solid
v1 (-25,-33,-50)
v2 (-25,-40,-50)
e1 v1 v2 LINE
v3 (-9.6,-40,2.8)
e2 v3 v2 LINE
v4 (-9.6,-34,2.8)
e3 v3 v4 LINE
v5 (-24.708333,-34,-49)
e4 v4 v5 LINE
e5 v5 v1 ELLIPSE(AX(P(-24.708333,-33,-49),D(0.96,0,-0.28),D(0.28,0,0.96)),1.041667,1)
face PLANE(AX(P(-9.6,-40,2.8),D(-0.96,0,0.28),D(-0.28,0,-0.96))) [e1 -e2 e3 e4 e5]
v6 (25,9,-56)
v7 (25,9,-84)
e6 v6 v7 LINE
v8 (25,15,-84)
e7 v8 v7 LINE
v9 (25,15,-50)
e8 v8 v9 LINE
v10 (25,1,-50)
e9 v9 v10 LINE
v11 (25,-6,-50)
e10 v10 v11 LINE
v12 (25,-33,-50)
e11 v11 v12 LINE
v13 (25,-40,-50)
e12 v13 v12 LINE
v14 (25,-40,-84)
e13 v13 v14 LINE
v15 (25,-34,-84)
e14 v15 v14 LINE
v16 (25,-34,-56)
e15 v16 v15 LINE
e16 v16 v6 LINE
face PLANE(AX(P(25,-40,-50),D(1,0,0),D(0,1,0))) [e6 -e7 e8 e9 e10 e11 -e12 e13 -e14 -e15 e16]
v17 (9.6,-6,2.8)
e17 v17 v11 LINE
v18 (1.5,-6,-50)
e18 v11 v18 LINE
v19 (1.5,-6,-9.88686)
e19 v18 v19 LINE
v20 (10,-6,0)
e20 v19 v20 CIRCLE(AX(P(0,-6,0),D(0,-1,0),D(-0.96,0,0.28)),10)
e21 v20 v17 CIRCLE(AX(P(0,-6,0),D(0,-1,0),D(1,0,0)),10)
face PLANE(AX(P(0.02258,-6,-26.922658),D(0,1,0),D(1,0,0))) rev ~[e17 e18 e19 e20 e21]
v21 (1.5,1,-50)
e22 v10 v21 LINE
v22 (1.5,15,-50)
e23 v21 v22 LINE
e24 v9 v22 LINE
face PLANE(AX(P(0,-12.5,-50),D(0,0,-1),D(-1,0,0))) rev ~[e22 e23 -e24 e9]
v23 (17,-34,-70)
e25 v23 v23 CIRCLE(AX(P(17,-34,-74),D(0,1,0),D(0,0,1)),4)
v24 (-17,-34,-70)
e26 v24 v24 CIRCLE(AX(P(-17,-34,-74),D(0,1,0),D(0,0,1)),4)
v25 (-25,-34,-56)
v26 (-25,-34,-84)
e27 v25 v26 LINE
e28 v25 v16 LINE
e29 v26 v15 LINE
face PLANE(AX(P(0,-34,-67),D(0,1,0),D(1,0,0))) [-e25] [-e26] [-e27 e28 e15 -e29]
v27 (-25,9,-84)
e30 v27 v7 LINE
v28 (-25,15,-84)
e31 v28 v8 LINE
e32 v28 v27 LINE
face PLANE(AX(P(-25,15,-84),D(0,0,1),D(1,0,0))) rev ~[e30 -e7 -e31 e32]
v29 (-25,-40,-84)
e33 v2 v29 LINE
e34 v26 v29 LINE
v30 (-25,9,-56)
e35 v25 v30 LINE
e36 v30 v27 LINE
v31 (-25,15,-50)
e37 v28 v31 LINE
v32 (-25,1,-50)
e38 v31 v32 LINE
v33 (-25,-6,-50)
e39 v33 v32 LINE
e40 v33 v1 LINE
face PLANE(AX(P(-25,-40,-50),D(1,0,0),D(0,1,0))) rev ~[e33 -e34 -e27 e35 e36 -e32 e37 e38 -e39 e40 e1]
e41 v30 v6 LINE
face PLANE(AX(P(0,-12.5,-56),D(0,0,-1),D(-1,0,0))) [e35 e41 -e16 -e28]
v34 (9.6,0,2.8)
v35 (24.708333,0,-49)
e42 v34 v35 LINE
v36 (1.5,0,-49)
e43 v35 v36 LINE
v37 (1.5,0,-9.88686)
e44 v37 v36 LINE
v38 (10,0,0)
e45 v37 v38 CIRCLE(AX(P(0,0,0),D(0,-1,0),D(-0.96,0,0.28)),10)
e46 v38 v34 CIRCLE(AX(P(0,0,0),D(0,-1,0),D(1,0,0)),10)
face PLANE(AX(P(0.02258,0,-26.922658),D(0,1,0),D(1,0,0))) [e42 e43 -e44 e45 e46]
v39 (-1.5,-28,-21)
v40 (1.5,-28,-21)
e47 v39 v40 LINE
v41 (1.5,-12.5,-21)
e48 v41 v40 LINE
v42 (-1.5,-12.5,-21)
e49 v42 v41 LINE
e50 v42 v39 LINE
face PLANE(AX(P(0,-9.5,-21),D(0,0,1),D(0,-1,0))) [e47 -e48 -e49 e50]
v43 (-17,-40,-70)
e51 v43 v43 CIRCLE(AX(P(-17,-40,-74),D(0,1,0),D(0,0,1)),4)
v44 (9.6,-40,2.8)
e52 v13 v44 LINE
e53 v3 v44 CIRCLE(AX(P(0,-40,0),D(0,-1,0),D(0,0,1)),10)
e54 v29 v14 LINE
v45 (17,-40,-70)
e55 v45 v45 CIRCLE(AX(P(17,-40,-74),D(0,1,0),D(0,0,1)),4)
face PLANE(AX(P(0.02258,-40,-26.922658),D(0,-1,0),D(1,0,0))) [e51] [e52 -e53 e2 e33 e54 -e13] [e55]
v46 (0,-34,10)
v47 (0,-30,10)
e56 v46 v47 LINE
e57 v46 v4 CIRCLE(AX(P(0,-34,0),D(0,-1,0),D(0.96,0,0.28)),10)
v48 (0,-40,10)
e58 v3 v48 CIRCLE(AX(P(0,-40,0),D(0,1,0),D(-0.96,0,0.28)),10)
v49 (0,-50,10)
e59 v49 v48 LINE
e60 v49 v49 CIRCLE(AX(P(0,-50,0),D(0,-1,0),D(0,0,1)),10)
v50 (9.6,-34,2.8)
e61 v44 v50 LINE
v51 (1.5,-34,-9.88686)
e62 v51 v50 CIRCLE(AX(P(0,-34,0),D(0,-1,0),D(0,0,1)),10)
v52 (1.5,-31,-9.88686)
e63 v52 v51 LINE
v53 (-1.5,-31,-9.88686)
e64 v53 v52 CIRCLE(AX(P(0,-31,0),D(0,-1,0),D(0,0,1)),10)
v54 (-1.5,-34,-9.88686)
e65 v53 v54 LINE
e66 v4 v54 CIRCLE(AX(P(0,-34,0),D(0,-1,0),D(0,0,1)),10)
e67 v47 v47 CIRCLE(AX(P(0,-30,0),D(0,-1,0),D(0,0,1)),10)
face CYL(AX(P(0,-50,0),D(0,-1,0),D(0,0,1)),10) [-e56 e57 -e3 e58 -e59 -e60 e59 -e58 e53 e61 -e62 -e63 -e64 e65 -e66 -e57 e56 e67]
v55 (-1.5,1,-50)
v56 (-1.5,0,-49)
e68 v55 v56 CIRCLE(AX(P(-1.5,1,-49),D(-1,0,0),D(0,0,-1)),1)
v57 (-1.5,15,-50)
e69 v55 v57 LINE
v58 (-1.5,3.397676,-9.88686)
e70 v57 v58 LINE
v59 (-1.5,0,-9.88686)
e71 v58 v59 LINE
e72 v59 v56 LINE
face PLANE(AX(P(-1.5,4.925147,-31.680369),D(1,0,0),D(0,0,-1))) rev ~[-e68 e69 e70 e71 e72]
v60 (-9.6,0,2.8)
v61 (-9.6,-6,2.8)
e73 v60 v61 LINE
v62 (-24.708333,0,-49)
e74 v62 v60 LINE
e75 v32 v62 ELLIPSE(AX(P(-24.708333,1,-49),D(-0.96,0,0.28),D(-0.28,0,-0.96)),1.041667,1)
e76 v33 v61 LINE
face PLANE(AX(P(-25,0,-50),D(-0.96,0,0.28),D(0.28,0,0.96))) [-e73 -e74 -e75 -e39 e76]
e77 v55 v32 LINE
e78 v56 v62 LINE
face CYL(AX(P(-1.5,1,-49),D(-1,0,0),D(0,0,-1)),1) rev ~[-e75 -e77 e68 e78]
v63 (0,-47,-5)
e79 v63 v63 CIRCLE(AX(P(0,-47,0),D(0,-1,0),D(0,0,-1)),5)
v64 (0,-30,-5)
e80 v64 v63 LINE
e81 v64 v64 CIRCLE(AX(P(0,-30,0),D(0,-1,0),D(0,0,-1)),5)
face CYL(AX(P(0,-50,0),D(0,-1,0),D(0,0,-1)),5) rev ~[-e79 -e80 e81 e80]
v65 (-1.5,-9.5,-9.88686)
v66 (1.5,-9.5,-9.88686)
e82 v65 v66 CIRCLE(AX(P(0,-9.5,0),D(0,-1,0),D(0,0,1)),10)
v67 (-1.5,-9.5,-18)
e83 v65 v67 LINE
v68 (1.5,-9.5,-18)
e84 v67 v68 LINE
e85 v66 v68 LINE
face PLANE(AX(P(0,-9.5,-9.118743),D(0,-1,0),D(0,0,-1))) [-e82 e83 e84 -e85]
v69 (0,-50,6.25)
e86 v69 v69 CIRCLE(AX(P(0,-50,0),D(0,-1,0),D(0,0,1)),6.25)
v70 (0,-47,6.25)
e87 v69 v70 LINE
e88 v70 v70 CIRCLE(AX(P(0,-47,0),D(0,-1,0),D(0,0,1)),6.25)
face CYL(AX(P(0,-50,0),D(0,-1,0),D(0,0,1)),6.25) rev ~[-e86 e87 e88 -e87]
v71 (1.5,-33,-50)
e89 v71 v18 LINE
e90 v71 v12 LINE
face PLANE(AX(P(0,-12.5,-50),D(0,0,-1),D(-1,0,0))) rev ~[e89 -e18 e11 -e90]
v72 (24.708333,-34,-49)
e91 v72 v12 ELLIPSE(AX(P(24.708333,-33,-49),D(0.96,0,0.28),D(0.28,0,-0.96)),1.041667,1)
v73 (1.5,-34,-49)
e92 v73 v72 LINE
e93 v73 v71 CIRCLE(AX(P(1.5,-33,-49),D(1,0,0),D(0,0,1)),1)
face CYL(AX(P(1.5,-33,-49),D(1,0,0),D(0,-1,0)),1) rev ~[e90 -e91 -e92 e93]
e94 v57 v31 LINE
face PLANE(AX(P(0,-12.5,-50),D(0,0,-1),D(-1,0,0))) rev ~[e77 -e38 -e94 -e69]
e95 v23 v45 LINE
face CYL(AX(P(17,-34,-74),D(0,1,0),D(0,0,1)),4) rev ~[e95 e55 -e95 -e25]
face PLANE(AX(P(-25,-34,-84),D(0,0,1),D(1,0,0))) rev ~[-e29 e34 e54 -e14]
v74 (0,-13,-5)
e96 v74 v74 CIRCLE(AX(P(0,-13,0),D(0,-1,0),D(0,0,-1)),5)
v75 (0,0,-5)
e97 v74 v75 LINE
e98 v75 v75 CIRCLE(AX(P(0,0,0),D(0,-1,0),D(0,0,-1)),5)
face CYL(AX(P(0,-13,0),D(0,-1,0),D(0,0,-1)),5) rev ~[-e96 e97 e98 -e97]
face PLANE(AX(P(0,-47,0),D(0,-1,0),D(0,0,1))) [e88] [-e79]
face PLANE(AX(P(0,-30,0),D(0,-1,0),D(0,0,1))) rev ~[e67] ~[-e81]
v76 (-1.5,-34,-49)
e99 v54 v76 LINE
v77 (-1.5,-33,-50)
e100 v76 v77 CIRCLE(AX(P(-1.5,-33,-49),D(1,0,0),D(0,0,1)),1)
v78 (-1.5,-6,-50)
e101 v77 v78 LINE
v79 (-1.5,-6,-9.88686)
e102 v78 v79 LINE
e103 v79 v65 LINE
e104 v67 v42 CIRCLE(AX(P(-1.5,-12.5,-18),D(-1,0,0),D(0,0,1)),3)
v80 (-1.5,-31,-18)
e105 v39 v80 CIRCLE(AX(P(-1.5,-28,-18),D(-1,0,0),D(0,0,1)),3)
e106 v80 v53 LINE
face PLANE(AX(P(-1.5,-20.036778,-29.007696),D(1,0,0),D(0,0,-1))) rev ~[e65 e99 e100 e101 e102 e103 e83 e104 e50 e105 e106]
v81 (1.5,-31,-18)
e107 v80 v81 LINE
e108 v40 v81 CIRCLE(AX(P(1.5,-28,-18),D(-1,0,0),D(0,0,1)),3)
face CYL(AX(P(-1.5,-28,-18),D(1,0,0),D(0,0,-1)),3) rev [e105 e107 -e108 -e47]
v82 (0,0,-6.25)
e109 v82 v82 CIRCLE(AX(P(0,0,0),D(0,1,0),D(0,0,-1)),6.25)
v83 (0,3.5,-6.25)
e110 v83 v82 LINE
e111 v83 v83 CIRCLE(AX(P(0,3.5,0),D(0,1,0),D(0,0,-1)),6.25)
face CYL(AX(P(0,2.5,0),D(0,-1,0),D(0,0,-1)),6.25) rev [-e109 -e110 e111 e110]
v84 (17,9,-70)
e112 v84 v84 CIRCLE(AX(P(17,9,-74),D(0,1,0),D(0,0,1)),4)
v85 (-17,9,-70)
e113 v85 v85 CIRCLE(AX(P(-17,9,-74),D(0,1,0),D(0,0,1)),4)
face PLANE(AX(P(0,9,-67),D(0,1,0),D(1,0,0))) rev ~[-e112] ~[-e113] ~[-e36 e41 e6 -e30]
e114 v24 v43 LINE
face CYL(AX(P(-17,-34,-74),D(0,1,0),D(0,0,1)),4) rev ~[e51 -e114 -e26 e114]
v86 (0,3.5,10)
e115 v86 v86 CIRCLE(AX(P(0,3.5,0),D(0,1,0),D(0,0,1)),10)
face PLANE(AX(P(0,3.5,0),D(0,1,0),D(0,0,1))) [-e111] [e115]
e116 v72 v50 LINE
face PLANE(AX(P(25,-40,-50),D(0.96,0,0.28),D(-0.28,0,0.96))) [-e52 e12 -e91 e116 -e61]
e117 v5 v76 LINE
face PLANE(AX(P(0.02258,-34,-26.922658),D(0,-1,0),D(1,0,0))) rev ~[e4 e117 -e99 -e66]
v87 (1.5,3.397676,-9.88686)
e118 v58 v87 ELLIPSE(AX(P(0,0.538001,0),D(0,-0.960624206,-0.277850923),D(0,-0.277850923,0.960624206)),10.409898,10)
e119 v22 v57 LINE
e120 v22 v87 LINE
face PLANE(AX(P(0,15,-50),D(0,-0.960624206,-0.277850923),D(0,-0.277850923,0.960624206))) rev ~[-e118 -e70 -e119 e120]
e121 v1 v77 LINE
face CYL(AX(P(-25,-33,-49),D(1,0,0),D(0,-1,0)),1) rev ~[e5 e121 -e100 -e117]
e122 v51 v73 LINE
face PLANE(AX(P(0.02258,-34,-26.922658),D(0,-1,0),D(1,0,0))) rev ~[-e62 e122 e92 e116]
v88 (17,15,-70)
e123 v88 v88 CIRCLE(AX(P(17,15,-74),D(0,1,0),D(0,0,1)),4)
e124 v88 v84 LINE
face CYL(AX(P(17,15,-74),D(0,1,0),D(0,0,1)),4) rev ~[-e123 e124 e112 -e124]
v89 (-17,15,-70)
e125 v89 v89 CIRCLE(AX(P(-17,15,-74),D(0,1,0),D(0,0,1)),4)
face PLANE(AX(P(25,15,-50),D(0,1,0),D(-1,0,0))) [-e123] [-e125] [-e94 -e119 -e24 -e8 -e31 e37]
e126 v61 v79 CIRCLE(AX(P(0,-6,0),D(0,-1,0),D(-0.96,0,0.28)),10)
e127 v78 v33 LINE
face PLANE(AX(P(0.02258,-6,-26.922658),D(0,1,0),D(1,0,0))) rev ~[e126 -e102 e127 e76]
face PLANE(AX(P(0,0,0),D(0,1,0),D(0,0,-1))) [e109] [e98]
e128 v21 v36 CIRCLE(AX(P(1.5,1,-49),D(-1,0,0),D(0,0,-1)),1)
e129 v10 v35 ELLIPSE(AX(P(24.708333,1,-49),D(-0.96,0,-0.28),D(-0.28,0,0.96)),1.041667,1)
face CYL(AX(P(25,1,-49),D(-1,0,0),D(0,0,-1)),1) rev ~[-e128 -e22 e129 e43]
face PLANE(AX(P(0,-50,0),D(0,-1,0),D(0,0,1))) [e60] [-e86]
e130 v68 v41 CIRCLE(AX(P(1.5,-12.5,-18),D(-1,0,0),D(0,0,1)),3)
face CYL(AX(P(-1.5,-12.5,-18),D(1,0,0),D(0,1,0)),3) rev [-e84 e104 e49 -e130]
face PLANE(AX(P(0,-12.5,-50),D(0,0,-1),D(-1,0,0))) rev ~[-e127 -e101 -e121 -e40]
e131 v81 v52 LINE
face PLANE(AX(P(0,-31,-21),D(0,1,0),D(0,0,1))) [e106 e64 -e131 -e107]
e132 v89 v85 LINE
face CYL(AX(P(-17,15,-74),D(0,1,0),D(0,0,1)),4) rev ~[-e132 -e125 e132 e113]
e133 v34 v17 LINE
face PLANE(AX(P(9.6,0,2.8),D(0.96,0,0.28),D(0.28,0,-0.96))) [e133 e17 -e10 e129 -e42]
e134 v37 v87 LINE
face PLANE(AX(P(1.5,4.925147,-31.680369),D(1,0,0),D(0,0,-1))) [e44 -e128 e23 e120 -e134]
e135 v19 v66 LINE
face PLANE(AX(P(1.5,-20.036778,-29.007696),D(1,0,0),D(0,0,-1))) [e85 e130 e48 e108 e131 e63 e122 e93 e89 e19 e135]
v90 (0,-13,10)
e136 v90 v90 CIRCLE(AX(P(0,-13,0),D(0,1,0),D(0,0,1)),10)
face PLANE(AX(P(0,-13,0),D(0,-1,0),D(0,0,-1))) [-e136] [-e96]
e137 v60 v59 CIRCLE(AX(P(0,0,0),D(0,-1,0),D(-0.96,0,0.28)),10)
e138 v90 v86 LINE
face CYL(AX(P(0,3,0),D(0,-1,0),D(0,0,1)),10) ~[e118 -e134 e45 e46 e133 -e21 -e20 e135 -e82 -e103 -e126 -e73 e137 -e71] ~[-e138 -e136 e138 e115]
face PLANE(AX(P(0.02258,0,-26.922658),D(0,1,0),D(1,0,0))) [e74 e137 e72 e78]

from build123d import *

# Parameters (mm, degrees)
BASE_PROFILE_SKETCH_R        = 10
BASE_PROFILE_SKETCH_R_2      = 6.25
BASE_PLATE_3MM_DEPTH         = 3
MOUNTING_WEB_6MM_DEPTH       = 6
BASE_START                   = -13
SKETCH1_4_R                  = 10
SKETCH1_4_R_2                = 6.25
BASE_BLOCK_13MM_DEPTH        = 13
SIDE_WALL_SKETCH_W           = 50
SIDE_WALL_SKETCH_H           = 55
SIDE_WALL_6MM_DEPTH          = 6
GUSSET_PROFILE_SKETCH_W      = 50
GUSSET_PROFILE_SKETCH_H      = 34
GUSSET_PROFILE_SKETCH_R      = 4
GUSSET_A_6MM_DEPTH           = 6
GUSSET_START                 = -49
SKETCH3_2_W                  = 50
SKETCH3_2_H                  = 34
SKETCH3_2_R                  = 4
GUSSET_B_6MM_DEPTH           = 6
CLEVIS_EYE_SKETCH_R          = 10
CLEVIS_EYE_SKETCH_R_2        = 5
CLEVIS_EYE_ARM_6MM_DEPTH     = 6
SKETCH4_3_R                  = 10
SKETCH4_3_R_2                = 5
CLEVIS_EYE_BOSS_A_10MM_DEPTH = 10
CLEVIS_START                 = 10
SKETCH4_4_R                  = 10
SKETCH4_4_R_2                = 5
CLEVIS_EYE_BOSS_B_10MM_DEPTH = 10
CLEVIS_PIVOT_BORE_SKETCH_R   = 6.25
CLEVIS_PIVOT_BORE_CUT_DEPTH  = 3
LOWER_PIVOT_BOSS_SKETCH_R    = 6.25
LOWER_PIVOT_BOSS_SKETCH_R_2  = 5
LOWER_PIVOT_BOSS_16MM_DEPTH  = 16
LOWER_START                  = -3
LOWER_PIVOT_BORE_SKETCH_R    = 6.25
LOWER_PIVOT_BORE_CUT_DEPTH   = 3
SUPPORT_RIB_3MM_DEPTH        = 1.5
SPOT_FACE_PAD_SKETCH_R       = 10
SPOT_FACE_PAD_0_5MM_DEPTH    = 0.5
PAD_START                    = -1
PAD_RECESS_SKETCH_R          = 6.25
PAD_RECESS_1MM_DEPTH         = 1
CLEVIS_EDGE_FILLET_R1_R      = 1
RIB_EDGE_FILLET_R3_R         = 3


with BuildPart() as part:
    # Base Profile Sketch → Base Plate 3mm (new body)
    with BuildSketch(Plane(origin=(0, 0, 0), x_dir=(1, 0, 0), z_dir=(0, 1, 0))):
        with Locations(Location((0, 0, 0), (0, 0, 270))):
            Circle(BASE_PROFILE_SKETCH_R)
        with Locations(Location((0, 0, 0), (0, 0, 270))):
            Circle(BASE_PROFILE_SKETCH_R_2, mode=Mode.SUBTRACT)
    extrude(amount=BASE_PLATE_3MM_DEPTH)



with BuildPart() as body_2:
    # Sketch1_3 → Mounting Web 6mm (new body)
    with BuildSketch(Plane(origin=(0, 0, 0), x_dir=(1, 0, 0), z_dir=(0, 1, 0))):
        with BuildLine():
            Line((25, 50), (-25, 50))
            Line((-25, 50), (-9.6, -2.8))
            ThreePointArc((-9.6, -2.8), (-1.414213562, 9.899494937), (10, 0))
            ThreePointArc((10, 0), (9.899494937, -1.414213562), (9.6, -2.8))
            Line((9.6, -2.8), (25, 50))
        make_face()
    extrude(amount=-MOUNTING_WEB_6MM_DEPTH)


with BuildPart() as part_1:
    add(part.part)

    add(body_2.part)  # Base Block 13mm merges body 2
    # Sketch1_4 → Base Block 13mm (add)
    with BuildSketch(Plane(origin=(0, 0, 0), x_dir=(1, 0, 0), z_dir=(0, 1, 0)).offset(BASE_START)):
        with Locations(Location((0, 0, 0), (0, 0, 270))):
            Circle(SKETCH1_4_R)
        with Locations(Location((0, 0, 0), (0, 0, 270))):
            Circle(SKETCH1_4_R_2, mode=Mode.SUBTRACT)
    extrude(amount=BASE_BLOCK_13MM_DEPTH)

    # Side Wall Sketch → Side Wall 6mm (add)
    with BuildSketch(Plane(origin=(0, 0, -50), x_dir=(-1, 0, 0), z_dir=(0, 0, -1))):
        with Locations((0, -12.5)):
            Rectangle(SIDE_WALL_SKETCH_W, SIDE_WALL_SKETCH_H)
    extrude(amount=SIDE_WALL_6MM_DEPTH)

    # Gusset Profile Sketch → Gusset A 6mm (add)
    with BuildSketch(Plane(origin=(0, 15, 0), x_dir=(1, 0, 0), z_dir=(0, 1, 0))):
        with Locations((0, 67)):
            Rectangle(GUSSET_PROFILE_SKETCH_W, GUSSET_PROFILE_SKETCH_H)
        with Locations(Location((-17, 74, 0), (0, 0, 270))):
            Circle(GUSSET_PROFILE_SKETCH_R, mode=Mode.SUBTRACT)
        with Locations(Location((17, 74, 0), (0, 0, 270))):
            Circle(GUSSET_PROFILE_SKETCH_R, mode=Mode.SUBTRACT)
    extrude(amount=-GUSSET_A_6MM_DEPTH)

    # Sketch3_2 → Gusset B 6mm (add)
    with BuildSketch(Plane(origin=(0, 15, 0), x_dir=(1, 0, 0), z_dir=(0, 1, 0)).offset(GUSSET_START)):
        with Locations((0, 67)):
            Rectangle(SKETCH3_2_W, SKETCH3_2_H)
        with Locations(Location((-17, 74, 0), (0, 0, 270))):
            Circle(SKETCH3_2_R, mode=Mode.SUBTRACT)
        with Locations(Location((17, 74, 0), (0, 0, 270))):
            Circle(SKETCH3_2_R, mode=Mode.SUBTRACT)
    extrude(amount=-GUSSET_B_6MM_DEPTH)

    # Clevis Eye Sketch → Clevis Eye Arm 6mm (add)
    # profile 1 of 2: a face of its own
    with BuildSketch(Plane.XZ.offset(40)):
        with BuildLine():
            Line((-9.6, 2.8), (-25, -50))
            Line((-25, -50), (25, -50))
            Line((25, -50), (9.6, 2.8))
            ThreePointArc((9.6, 2.8), (9.899494937, 1.414213562), (10, 0))
            ThreePointArc((10, 0), (-1.414213562, -9.899494937), (-9.6, 2.8))
        make_face()
    # profile 2 of 2: a face of its own
    with BuildSketch(Plane.XZ.offset(40)):
        with Locations(Location((0, 0, 0), (0, 0, 90))):
            Circle(CLEVIS_EYE_SKETCH_R)
        with Locations(Location((0, 0, 0), (0, 0, 270))):
            Circle(CLEVIS_EYE_SKETCH_R_2, mode=Mode.SUBTRACT)
    extrude(amount=-CLEVIS_EYE_ARM_6MM_DEPTH)

    # Sketch4_3 → Clevis Eye Boss A 10mm (add)
    with BuildSketch(Plane.XZ.offset(40)):
        with Locations(Location((0, 0, 0), (0, 0, 90))):
            Circle(SKETCH4_3_R)
        with Locations(Location((0, 0, 0), (0, 0, 270))):
            Circle(SKETCH4_3_R_2, mode=Mode.SUBTRACT)
    extrude(amount=-CLEVIS_EYE_BOSS_A_10MM_DEPTH)

    # Sketch4_4 → Clevis Eye Boss B 10mm (add)
    with BuildSketch(Plane.XZ.offset(40).offset(CLEVIS_START)):
        with Locations(Location((0, 0, 0), (0, 0, 90))):
            Circle(SKETCH4_4_R)
        with Locations(Location((0, 0, 0), (0, 0, 270))):
            Circle(SKETCH4_4_R_2, mode=Mode.SUBTRACT)
    extrude(amount=-CLEVIS_EYE_BOSS_B_10MM_DEPTH)

    # Clevis Pivot Bore Sketch → Clevis Pivot Bore Cut (cut)
    with BuildSketch(Plane.XZ.offset(50)):
        with Locations(Location((0, 0, 0), (0, 0, 90))):
            Circle(CLEVIS_PIVOT_BORE_SKETCH_R)
    extrude(amount=-CLEVIS_PIVOT_BORE_CUT_DEPTH, mode=Mode.SUBTRACT)

    # Lower Pivot Boss Sketch → Lower Pivot Boss 16mm (add)
    with BuildSketch(Plane.XZ.offset(13)):
        with Locations(Location((0, 0, 0), (0, 0, 270))):
            Circle(LOWER_PIVOT_BOSS_SKETCH_R)
        with Locations(Location((0, 0, 0), (0, 0, 270))):
            Circle(LOWER_PIVOT_BOSS_SKETCH_R_2, mode=Mode.SUBTRACT)
    extrude(amount=-LOWER_PIVOT_BOSS_16MM_DEPTH)

    # Lower Pivot Bore Sketch → Lower Pivot Bore Cut (cut)
    with BuildSketch(Plane(origin=(0, 3, 0), x_dir=(1, 0, 0), z_dir=(0, 1, 0)).offset(LOWER_START)):
        with Locations(Location((0, 0, 0), (0, 0, 90))):
            Circle(LOWER_PIVOT_BORE_SKETCH_R)
    extrude(amount=LOWER_PIVOT_BORE_CUT_DEPTH, mode=Mode.SUBTRACT)

    # Support Rib Sketch → Support Rib 3mm (add, symmetric)
    with BuildSketch(Plane(origin=(0, 0, 0), x_dir=(0, 0, -1), z_dir=(1, 0, 0))):
        Polygon((50, 15), (8.511959117, 3), (8.511959117, 0), (50, 0), align=None)
        Polygon((9.118743045, -9.5), (21, -9.5), (21, -31), (9.118743045, -31), (9.118743045, -34), (50, -34), (50, -6), (9.118743045, -6), align=None)
    extrude(amount=SUPPORT_RIB_3MM_DEPTH, both=True)

    # Spot Face Pad Sketch → Spot Face Pad 0.5mm (add)
    with BuildSketch(Plane(origin=(0, 3, 0), x_dir=(1, 0, 0), z_dir=(0, 1, 0))):
        with Locations(Location((0, 0, 0), (0, 0, 270))):
            Circle(SPOT_FACE_PAD_SKETCH_R)
    extrude(amount=SPOT_FACE_PAD_0_5MM_DEPTH)

    # Pad Recess Sketch → Pad Recess 1mm (cut)
    with BuildSketch(Plane(origin=(0, 3.5, 0), x_dir=(1, 0, 0), z_dir=(0, 1, 0)).offset(PAD_START)):
        with Locations(Location((0, 0, 0), (0, 0, 90))):
            Circle(PAD_RECESS_SKETCH_R)
    extrude(amount=PAD_RECESS_1MM_DEPTH, mode=Mode.SUBTRACT)

    # Clevis Edge Fillet R1
    clevis_edge_fillet_r1_edges = [part_1.edges().sort_by_distance(p)[0] for p in [
        (13.25, 0, -50),
        (-13.25, 0, -50),
        (-13.25, -34, -50),
        (13.25, -34, -50),
    ]]
    fillet(clevis_edge_fillet_r1_edges, radius=CLEVIS_EDGE_FILLET_R1_R)

    # Rib Edge Fillet R3
    rib_edge_fillet_r3_edges = [part_1.edges().sort_by_distance(p)[0] for p in [
        (0, -9.5, -21),
        (0, -31, -21),
    ]]
    fillet(rib_edge_fillet_r3_edges, radius=RIB_EDGE_FILLET_R3_R)


solid = part_1.part
